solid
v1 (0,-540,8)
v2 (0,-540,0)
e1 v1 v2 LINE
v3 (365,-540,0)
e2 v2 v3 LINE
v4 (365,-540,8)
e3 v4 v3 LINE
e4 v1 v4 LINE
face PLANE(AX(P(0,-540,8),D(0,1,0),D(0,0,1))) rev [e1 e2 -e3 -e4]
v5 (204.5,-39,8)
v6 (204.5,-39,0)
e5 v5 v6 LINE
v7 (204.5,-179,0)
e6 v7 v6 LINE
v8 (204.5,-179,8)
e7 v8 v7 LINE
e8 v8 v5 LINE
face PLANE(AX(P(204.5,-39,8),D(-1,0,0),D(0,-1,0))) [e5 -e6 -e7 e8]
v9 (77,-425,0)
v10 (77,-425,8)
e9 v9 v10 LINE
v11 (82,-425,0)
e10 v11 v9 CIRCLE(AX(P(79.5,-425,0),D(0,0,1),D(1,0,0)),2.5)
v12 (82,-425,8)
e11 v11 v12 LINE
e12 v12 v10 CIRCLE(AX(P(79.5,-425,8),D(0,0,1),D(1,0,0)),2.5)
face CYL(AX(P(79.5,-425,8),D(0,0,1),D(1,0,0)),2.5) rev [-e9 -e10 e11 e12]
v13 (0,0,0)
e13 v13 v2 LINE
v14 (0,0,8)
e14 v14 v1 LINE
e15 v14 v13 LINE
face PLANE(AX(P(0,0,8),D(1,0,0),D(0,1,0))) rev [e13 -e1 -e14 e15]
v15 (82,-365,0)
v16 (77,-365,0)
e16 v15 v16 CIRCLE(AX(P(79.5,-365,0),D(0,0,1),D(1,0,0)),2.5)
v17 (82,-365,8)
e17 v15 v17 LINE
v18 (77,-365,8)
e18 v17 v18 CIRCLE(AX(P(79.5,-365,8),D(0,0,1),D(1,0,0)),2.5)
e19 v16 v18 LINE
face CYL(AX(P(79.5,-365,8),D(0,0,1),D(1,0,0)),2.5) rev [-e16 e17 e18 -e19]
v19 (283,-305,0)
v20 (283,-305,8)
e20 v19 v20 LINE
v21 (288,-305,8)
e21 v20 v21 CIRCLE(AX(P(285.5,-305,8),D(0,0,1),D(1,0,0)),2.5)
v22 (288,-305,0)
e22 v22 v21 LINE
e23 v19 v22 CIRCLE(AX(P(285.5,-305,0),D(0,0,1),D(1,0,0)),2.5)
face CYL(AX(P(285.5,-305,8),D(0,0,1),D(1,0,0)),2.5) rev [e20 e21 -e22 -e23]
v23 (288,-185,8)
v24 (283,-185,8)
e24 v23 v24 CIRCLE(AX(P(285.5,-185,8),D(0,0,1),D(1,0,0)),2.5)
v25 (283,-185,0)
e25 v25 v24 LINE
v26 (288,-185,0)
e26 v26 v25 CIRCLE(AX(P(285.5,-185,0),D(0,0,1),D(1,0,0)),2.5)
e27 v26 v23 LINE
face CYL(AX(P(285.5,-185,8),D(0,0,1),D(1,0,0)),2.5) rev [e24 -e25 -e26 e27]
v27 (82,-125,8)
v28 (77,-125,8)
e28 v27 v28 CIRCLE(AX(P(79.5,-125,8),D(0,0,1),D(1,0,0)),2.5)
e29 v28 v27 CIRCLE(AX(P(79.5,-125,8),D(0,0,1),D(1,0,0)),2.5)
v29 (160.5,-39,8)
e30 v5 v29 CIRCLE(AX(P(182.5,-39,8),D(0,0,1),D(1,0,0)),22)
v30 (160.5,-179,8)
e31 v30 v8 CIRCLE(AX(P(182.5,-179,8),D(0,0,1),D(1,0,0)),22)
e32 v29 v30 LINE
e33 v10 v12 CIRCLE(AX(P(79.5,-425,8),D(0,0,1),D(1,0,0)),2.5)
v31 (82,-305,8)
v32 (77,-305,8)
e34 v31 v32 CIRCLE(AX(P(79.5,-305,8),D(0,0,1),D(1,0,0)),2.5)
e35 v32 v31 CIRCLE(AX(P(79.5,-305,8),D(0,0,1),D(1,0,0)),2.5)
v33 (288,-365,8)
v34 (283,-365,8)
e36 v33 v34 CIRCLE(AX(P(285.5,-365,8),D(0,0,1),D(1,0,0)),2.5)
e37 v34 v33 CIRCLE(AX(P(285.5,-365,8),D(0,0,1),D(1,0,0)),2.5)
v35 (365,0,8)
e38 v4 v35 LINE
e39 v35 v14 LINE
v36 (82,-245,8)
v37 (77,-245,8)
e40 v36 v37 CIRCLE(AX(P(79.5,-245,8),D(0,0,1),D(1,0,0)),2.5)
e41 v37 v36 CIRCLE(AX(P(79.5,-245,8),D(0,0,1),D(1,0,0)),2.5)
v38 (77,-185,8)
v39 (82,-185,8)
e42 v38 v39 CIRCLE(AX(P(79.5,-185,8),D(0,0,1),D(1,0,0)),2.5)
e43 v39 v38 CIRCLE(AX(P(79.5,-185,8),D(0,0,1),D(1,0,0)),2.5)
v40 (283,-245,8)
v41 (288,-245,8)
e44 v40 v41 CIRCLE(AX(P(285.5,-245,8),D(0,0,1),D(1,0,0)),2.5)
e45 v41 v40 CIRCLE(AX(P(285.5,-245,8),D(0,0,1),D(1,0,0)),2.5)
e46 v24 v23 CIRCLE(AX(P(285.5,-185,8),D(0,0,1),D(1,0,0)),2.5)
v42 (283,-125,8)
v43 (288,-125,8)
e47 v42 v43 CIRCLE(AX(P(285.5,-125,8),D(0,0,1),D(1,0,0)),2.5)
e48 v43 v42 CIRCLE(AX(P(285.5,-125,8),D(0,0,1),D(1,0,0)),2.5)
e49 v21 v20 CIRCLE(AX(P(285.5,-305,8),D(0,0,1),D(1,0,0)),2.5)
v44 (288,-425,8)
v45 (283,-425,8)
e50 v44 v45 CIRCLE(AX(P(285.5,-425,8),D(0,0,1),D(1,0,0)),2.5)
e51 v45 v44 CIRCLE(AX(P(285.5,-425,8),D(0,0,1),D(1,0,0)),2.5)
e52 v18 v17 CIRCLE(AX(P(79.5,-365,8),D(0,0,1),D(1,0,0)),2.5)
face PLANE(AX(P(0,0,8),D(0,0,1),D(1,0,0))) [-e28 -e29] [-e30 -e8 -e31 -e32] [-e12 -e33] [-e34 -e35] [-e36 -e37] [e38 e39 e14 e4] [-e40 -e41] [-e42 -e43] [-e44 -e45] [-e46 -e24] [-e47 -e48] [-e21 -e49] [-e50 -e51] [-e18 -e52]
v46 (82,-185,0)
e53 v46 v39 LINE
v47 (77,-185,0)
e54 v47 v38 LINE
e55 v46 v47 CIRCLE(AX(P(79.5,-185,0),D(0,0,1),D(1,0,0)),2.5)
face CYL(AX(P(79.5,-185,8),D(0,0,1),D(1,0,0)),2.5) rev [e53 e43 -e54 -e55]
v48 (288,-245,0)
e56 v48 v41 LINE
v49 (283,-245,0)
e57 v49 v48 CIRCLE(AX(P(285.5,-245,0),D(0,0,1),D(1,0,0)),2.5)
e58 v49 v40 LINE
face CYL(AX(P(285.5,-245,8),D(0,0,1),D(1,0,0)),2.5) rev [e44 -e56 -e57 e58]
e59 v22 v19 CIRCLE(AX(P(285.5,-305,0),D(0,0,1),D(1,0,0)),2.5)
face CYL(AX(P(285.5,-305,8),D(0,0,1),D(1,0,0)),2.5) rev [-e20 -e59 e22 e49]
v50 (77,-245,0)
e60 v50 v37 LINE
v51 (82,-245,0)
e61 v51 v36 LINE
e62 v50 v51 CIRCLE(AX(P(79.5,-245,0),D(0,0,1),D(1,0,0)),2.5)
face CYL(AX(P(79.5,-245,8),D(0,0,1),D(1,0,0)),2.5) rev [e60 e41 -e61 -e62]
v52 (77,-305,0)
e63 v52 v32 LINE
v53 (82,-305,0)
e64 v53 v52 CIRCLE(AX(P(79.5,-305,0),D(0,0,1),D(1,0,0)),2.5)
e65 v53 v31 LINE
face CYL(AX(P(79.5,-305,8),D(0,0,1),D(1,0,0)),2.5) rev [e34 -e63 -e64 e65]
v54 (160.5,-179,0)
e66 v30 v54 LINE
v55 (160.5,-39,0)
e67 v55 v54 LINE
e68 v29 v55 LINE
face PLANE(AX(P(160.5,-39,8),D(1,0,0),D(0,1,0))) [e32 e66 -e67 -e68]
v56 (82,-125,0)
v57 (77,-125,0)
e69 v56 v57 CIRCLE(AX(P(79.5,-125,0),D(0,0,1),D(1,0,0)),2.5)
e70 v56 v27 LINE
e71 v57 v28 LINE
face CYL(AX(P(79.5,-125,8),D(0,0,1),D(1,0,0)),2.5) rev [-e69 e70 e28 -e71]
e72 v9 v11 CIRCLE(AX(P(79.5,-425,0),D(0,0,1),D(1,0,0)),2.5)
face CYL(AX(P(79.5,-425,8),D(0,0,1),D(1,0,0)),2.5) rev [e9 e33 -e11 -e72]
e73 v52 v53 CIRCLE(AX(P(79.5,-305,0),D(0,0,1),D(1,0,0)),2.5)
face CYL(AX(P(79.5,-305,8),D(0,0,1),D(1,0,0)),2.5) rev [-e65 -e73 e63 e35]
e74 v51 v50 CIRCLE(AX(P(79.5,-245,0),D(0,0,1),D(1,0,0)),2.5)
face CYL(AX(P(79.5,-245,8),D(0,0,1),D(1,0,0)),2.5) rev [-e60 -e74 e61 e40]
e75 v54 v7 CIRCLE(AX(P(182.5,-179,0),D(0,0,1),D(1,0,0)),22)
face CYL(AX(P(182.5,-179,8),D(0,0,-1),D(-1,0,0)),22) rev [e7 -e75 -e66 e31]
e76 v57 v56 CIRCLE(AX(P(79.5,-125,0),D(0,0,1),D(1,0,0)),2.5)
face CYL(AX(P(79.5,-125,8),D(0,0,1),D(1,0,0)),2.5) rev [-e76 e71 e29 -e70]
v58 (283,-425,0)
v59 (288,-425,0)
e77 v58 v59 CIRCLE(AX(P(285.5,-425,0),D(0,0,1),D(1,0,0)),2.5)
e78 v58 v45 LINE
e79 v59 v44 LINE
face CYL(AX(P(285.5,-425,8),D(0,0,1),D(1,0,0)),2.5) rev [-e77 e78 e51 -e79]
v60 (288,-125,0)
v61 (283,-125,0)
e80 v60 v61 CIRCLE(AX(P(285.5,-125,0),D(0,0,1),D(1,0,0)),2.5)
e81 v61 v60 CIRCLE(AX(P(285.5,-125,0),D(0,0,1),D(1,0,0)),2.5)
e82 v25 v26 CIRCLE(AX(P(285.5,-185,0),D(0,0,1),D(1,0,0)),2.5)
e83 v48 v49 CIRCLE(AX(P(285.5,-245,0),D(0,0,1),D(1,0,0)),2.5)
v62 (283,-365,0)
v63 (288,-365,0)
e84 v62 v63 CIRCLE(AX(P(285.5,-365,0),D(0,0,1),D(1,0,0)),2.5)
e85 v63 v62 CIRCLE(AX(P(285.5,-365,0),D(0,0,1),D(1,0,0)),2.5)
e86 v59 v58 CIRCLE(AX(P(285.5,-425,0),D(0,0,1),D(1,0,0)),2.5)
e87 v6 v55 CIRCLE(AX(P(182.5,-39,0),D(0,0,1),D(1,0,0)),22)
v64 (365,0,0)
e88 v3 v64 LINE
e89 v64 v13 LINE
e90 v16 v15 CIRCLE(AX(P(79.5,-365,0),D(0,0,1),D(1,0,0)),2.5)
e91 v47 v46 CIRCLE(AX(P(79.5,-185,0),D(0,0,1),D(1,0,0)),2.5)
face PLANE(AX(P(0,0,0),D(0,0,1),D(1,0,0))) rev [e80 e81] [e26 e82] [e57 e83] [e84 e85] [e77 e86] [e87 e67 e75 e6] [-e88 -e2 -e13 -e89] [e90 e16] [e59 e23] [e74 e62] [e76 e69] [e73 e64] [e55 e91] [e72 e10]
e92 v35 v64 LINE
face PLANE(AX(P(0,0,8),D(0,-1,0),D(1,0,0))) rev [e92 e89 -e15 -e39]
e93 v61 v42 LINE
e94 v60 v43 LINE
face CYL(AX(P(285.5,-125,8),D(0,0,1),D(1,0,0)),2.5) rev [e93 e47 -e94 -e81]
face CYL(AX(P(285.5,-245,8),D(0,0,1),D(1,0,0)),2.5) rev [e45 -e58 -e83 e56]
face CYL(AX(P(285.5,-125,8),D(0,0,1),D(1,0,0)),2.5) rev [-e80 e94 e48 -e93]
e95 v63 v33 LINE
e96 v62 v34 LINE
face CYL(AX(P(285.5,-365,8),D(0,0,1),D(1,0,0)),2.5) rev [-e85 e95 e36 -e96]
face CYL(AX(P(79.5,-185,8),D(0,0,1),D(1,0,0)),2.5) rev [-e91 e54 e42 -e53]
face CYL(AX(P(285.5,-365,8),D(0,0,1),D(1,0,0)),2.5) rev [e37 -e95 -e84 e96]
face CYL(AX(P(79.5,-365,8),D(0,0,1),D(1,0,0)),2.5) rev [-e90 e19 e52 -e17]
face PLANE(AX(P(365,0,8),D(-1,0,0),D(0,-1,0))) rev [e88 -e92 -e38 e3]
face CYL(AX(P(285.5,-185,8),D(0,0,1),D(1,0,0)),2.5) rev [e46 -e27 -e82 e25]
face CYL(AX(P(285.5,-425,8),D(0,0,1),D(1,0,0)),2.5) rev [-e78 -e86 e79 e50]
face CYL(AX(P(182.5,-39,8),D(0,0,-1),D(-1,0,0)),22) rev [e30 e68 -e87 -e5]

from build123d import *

# Parameters (mm, degrees)
SKETCH1_W           = 365
SKETCH1_H           = 540
BOSS_EXTRUDE1_DEPTH = 8
M6_TAPPED_HOLE1_D   = 5
LPATTERN1_COUNT     = 6
LPATTERN1_PITCH     = 60


with BuildPart() as part:
    # Sketch1 → Boss-Extrude1 (new body)
    with BuildSketch(Plane.XY):
        with Locations((182.5, -270)):
            Rectangle(SKETCH1_W, SKETCH1_H)
        with BuildLine():
            Line((204.5, -39), (204.5, -179))
            ThreePointArc((204.5, -179), (182.5, -201), (160.5, -179))
            Line((160.5, -179), (160.5, -39))
            ThreePointArc((160.5, -39), (182.5, -17), (204.5, -39))
        make_face(mode=Mode.SUBTRACT)
    extrude(amount=BOSS_EXTRUDE1_DEPTH)

    # M6 Tapped Hole1 (through all)
    with Locations(Plane.XY.offset(8)):
        with Locations((79.5, -125), (285.5, -125)):
            m6_tapped_hole1 = Hole(M6_TAPPED_HOLE1_D / 2)

    # LPattern1: M6 Tapped Hole1 ×6
    with Locations(*[(0, -i * LPATTERN1_PITCH, 0) for i in range(1, LPATTERN1_COUNT)]):
        add(m6_tapped_hole1, mode=Mode.SUBTRACT)


solid = part.part
